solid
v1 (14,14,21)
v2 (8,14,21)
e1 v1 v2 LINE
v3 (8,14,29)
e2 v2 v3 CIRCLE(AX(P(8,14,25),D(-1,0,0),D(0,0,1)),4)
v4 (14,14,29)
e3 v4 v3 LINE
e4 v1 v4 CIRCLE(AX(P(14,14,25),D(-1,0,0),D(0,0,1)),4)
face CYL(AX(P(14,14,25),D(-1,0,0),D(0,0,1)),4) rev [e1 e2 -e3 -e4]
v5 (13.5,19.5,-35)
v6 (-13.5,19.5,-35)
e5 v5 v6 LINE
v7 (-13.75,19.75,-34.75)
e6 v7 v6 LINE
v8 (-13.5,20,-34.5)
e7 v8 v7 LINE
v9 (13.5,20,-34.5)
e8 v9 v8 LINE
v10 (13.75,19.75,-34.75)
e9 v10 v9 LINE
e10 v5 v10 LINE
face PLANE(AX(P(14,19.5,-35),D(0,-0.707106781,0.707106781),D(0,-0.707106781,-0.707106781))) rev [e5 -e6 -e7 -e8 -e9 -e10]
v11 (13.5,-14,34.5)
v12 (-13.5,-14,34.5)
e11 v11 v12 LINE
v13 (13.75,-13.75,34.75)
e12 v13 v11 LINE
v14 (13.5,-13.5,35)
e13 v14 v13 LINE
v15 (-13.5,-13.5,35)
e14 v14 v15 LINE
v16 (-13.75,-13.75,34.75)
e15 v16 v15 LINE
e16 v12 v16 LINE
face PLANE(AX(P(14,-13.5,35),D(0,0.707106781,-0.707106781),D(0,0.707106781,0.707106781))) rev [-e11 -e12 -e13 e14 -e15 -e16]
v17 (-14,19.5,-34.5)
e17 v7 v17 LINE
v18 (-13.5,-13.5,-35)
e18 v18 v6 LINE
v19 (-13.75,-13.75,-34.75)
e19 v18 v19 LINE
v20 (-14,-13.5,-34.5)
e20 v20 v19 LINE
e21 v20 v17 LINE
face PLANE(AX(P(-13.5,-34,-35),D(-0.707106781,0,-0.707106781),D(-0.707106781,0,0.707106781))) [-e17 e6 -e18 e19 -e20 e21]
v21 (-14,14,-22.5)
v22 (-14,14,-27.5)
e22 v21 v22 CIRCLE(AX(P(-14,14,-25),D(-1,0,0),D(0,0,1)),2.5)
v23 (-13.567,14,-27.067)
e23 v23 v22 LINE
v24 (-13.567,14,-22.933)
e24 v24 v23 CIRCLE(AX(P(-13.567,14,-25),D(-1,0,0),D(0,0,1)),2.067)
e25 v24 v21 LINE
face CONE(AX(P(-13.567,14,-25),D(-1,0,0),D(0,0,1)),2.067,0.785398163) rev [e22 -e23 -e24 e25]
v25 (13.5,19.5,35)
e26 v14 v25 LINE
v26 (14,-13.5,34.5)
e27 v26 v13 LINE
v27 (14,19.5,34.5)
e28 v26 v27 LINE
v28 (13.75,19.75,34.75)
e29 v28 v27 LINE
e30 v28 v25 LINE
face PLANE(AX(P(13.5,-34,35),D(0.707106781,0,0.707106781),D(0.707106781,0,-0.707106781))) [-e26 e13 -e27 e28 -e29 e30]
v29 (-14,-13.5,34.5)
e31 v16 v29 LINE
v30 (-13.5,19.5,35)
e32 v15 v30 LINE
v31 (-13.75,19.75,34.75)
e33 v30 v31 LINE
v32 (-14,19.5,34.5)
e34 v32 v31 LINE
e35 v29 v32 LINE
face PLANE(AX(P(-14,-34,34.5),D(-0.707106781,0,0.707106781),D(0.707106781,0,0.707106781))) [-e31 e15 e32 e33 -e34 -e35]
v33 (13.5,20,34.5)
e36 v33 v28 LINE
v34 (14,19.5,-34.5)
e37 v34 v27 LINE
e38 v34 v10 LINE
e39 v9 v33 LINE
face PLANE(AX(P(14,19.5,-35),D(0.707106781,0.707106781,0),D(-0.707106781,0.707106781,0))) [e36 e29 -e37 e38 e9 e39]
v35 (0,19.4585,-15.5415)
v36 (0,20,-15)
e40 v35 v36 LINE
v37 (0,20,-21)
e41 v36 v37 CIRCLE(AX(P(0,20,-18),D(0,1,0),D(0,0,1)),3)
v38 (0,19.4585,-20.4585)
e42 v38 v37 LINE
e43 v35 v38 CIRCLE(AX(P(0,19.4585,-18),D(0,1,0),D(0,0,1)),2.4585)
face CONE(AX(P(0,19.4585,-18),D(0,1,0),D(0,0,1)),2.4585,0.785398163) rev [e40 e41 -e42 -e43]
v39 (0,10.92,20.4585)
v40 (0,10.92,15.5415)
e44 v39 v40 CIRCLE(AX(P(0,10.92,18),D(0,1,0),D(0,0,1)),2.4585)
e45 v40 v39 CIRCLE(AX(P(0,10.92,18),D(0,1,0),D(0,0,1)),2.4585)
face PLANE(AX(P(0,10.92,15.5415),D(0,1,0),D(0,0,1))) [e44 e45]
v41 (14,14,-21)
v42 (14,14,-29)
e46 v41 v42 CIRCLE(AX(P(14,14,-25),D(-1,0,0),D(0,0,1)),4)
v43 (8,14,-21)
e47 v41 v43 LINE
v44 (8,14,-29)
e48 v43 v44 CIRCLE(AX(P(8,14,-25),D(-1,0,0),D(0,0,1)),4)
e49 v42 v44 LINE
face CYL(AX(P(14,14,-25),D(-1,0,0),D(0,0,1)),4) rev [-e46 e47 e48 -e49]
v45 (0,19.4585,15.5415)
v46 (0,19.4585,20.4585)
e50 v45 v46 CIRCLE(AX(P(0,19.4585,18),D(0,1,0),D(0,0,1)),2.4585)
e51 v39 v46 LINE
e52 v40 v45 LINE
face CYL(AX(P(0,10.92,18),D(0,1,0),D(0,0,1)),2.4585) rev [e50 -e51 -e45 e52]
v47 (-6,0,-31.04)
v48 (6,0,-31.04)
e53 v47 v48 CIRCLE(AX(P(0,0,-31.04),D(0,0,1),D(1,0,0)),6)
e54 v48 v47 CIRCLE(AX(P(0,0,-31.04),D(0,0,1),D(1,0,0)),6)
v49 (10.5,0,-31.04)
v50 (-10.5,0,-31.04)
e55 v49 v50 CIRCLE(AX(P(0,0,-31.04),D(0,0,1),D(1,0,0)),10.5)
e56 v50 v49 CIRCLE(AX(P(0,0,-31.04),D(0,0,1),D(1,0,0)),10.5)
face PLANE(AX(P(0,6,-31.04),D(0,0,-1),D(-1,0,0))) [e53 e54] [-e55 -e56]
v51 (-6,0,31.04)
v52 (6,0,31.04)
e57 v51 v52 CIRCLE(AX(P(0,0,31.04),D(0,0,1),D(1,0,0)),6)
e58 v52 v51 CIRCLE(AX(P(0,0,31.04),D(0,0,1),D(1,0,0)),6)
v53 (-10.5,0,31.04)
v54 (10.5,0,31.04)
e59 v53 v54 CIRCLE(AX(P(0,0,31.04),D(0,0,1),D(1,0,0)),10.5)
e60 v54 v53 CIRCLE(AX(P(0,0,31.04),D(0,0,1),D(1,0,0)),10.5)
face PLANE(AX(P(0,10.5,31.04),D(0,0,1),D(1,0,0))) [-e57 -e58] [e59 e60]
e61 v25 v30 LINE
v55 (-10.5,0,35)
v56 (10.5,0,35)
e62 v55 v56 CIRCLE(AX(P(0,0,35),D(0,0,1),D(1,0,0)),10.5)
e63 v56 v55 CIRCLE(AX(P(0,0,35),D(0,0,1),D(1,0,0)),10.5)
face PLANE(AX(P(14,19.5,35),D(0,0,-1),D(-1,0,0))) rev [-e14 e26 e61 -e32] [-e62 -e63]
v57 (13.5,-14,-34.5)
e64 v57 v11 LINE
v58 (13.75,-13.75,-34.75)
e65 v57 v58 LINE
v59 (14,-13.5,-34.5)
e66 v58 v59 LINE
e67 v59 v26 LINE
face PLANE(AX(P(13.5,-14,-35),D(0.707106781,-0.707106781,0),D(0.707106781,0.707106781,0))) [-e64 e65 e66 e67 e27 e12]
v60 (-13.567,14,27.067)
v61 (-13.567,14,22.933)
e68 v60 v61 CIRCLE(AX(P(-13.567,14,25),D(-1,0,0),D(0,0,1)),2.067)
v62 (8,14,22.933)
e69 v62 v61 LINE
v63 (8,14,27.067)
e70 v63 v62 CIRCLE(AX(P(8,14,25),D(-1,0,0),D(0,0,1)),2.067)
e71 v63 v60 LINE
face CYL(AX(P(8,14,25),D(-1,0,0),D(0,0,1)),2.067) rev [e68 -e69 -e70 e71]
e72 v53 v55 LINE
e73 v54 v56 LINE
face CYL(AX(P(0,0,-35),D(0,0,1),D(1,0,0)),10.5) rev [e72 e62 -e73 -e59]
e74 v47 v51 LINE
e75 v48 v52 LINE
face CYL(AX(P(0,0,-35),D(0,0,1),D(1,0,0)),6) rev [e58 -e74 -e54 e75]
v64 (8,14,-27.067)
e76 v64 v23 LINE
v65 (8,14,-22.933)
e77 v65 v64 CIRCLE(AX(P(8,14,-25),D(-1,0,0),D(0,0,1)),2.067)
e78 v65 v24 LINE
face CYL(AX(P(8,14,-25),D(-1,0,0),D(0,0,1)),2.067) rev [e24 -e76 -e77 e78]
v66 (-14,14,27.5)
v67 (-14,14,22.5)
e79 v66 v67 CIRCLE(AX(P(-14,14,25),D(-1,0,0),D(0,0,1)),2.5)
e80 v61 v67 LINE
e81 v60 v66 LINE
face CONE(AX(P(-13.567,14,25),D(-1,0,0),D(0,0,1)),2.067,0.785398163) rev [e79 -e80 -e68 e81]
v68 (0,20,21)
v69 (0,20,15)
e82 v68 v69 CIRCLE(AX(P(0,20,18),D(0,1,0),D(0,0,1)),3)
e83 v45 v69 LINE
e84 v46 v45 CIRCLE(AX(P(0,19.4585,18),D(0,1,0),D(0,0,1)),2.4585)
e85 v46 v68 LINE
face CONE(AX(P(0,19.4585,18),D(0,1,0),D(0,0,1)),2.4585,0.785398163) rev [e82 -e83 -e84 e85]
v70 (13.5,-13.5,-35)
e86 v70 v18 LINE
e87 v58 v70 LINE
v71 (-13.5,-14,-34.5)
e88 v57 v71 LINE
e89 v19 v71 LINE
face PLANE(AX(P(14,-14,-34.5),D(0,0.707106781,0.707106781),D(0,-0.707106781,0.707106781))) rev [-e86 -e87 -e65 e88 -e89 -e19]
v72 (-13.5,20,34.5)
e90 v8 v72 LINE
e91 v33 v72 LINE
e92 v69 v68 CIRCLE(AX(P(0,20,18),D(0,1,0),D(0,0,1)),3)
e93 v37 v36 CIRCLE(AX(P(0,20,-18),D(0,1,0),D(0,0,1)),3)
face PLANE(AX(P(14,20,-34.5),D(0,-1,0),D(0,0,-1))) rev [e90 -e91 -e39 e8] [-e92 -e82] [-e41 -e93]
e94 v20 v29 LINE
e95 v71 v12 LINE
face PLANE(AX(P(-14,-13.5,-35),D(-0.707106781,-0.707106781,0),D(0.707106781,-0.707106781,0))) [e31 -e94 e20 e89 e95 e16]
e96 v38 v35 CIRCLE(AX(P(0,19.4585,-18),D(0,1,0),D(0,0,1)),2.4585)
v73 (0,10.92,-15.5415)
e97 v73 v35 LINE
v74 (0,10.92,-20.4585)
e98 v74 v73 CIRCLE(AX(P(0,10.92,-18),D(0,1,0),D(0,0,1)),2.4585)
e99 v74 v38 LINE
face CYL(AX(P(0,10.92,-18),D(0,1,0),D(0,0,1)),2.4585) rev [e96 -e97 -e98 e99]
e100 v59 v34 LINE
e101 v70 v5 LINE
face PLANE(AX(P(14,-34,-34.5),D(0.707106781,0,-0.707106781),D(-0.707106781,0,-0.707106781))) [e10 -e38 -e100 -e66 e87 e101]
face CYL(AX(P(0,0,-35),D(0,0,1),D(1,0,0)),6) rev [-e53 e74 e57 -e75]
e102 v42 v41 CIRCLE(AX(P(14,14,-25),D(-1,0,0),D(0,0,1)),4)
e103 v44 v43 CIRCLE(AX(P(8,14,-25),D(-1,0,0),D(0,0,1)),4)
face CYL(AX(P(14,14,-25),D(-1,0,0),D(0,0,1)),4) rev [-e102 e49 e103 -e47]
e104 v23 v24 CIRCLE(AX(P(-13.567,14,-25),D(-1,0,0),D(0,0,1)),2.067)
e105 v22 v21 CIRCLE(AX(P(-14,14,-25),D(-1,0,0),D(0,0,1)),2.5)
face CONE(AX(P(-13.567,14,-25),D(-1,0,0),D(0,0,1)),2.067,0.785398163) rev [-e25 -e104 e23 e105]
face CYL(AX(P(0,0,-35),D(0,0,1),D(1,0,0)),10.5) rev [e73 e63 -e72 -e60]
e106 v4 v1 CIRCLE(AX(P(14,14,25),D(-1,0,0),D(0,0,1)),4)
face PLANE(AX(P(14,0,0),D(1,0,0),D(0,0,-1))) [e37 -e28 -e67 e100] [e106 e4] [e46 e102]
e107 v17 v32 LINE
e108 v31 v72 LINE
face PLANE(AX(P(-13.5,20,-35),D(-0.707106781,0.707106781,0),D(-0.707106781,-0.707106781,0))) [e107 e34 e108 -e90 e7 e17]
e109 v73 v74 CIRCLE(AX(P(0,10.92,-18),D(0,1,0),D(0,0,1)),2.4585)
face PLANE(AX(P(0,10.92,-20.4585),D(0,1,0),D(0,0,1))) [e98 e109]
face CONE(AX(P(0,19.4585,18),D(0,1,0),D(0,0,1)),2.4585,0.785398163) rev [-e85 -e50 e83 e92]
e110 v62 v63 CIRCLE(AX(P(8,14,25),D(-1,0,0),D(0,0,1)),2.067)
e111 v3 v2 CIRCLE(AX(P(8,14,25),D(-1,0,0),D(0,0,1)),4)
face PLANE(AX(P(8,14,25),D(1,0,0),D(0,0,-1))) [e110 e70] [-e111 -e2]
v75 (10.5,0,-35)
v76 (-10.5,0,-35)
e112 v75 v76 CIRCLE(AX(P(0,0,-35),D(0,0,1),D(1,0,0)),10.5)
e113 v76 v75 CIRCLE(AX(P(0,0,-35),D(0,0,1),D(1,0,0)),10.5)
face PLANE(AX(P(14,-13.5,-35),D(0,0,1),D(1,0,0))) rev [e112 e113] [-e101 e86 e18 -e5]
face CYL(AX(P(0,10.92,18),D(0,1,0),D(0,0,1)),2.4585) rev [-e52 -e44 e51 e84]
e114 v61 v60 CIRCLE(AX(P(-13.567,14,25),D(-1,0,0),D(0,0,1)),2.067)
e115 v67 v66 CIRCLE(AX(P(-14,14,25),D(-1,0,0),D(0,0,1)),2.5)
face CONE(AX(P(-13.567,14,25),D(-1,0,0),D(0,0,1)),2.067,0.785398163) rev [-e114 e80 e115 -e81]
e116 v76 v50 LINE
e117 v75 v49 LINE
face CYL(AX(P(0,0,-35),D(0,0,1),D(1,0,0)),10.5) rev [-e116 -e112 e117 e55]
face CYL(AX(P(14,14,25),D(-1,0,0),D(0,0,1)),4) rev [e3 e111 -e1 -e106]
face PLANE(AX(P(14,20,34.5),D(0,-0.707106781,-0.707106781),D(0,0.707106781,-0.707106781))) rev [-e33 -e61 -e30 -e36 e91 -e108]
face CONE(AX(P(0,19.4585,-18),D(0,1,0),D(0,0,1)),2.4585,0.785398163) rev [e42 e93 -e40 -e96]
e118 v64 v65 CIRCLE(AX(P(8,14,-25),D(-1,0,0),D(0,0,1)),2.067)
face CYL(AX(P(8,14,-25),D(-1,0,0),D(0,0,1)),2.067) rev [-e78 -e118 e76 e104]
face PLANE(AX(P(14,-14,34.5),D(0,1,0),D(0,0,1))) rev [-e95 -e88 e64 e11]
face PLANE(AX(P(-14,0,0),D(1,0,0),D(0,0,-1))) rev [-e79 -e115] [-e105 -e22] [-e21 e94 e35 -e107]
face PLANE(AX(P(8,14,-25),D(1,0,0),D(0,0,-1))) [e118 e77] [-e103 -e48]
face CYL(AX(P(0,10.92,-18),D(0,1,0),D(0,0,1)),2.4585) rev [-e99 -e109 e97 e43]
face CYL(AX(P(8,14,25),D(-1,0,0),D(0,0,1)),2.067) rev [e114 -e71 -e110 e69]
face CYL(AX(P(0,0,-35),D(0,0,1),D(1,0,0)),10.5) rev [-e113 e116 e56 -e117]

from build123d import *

# Parameters (mm, degrees)
EXTRUDE_1_DEPTH          = 14
EXTRUDE_1_DEPTH_BACK     = 14
SKETCH_3_W               = 6
SKETCH_3_H               = 4
SKETCH_4_W               = 6
SKETCH_4_H               = 4
CUT_EXTRUDE_1_DEPTH      = 35
CUT_EXTRUDE_1_DEPTH_BACK = 35
SKETCH_9_W               = 32
SKETCH_9_H               = 38
CUT_EXTRUDE_2_DEPTH      = 34
CUT_EXTRUDE_2_DEPTH_BACK = 34
SKETCH_10_W              = 32
SKETCH_10_H              = 74


with BuildPart() as part:
    # 草图1 → 凸台-拉伸1 (new, two sides: drawn at the far end of the back side and taken through both)
    with BuildSketch(Plane(origin=(0, 0, 0), x_dir=(0, 0, -1), z_dir=(1, 0, 0)).offset(-EXTRUDE_1_DEPTH_BACK)):
        Polygon((-35, -13.5), (-34.5, -14), (34.5, -14), (35, -13.5), (35, 19.5), (34.5, 20), (-34.5, 20), (-35, 19.5), align=None)
    extrude(amount=EXTRUDE_1_DEPTH + EXTRUDE_1_DEPTH_BACK)

    # 草图2 → 切除-旋转1 (revolve, cut)
    with BuildSketch(Plane(origin=(0, 0, 0), x_dir=(0, 0, -1), z_dir=(1, 0, 0)), mode=Mode.PRIVATE) as cut_revolve_1_sk:
        Polygon((-35, 0), (-35, 10.5), (-31.04, 10.5), (-31.04, 6), (31.04, 6), (31.04, 10.5), (35, 10.5), (35, 0), align=None)
    revolve(cut_revolve_1_sk.sketch.rotate(Axis((0, 0, -35), (0, 0, 1)), 270), axis=Axis((0, 0, -35), (0, 0, 1)), mode=Mode.SUBTRACT)

    # 草图3 → 切除-旋转2 (revolve, cut)
    with BuildSketch(Plane.XY.offset(25), mode=Mode.PRIVATE) as cut_revolve_2_sk:
        with Locations((11, 16)):
            Rectangle(SKETCH_3_W, SKETCH_3_H)
    revolve(cut_revolve_2_sk.sketch.rotate(Axis((14, 14, 25), (-1, 0, 0)), 270), axis=Axis((14, 14, 25), (-1, 0, 0)), mode=Mode.SUBTRACT)

    # 草图4 → 切除-旋转3 (revolve, cut)
    with BuildSketch(Plane.XY.offset(-25), mode=Mode.PRIVATE) as cut_revolve_3_sk:
        with Locations((11, 16)):
            Rectangle(SKETCH_4_W, SKETCH_4_H)
    revolve(cut_revolve_3_sk.sketch.rotate(Axis((14, 14, -25), (-1, 0, 0)), 270), axis=Axis((14, 14, -25), (-1, 0, 0)), mode=Mode.SUBTRACT)

    # 草图5 → 切除-旋转4 (revolve, cut)
    with BuildSketch(Plane(origin=(0, 0, 0), x_dir=(0, 0, -1), z_dir=(1, 0, 0)), mode=Mode.PRIVATE) as cut_revolve_4_sk:
        Polygon((18, 20), (21, 20), (20.4585, 19.4585), (20.4585, 10.92), (18, 10.92), align=None)
    revolve(cut_revolve_4_sk.sketch.rotate(Axis((0, 10.92, -18), (0, 1, 0)), 180), axis=Axis((0, 10.92, -18), (0, 1, 0)), mode=Mode.SUBTRACT)

    # 草图6 → 切除-旋转5 (revolve, cut)
    with BuildSketch(Plane(origin=(0, 0, 0), x_dir=(0, 0, -1), z_dir=(1, 0, 0)), mode=Mode.PRIVATE) as cut_revolve_5_sk:
        Polygon((-18, 20), (-15, 20), (-15.5415, 19.4585), (-15.5415, 10.92), (-18, 10.92), align=None)
    revolve(cut_revolve_5_sk.sketch.rotate(Axis((0, 10.92, 18), (0, 1, 0)), 180), axis=Axis((0, 10.92, 18), (0, 1, 0)), mode=Mode.SUBTRACT)

    # 草图7 → 切除-旋转6 (revolve, cut)
    with BuildSketch(Plane.XY.offset(-25), mode=Mode.PRIVATE) as cut_revolve_6_sk:
        Polygon((-14, 14), (-14, 16.5), (-13.567, 16.067), (8, 16.067), (8, 14), align=None)
    revolve(cut_revolve_6_sk.sketch.rotate(Axis((8, 14, -25), (-1, 0, 0)), 270), axis=Axis((8, 14, -25), (-1, 0, 0)), mode=Mode.SUBTRACT)

    # 草图8 → 切除-旋转7 (revolve, cut)
    with BuildSketch(Plane.XY.offset(25), mode=Mode.PRIVATE) as cut_revolve_7_sk:
        Polygon((-14, 14), (-14, 16.5), (-13.567, 16.067), (8, 16.067), (8, 14), align=None)
    revolve(cut_revolve_7_sk.sketch.rotate(Axis((8, 14, 25), (-1, 0, 0)), 270), axis=Axis((8, 14, 25), (-1, 0, 0)), mode=Mode.SUBTRACT)

    # 草图9 → 切除-拉伸1 (cut, two sides: drawn at the far end of the back side and taken through both)
    with BuildSketch(Plane.XY.offset(-CUT_EXTRUDE_1_DEPTH_BACK)):
        with Locations((0, 3)):
            Rectangle(SKETCH_9_W, SKETCH_9_H)
        Polygon((-14, -13.5), (-13.5, -14), (13.5, -14), (14, -13.5), (14, 19.5), (13.5, 20), (-13.5, 20), (-14, 19.5), align=None, mode=Mode.SUBTRACT)
    extrude(amount=CUT_EXTRUDE_1_DEPTH + CUT_EXTRUDE_1_DEPTH_BACK, mode=Mode.SUBTRACT)

    # 草图10 → 切除-拉伸2 (cut, two sides: drawn at the far end of the back side and taken through both)
    with BuildSketch(Plane(origin=(0, 0, 0), x_dir=(1, 0, 0), z_dir=(0, 1, 0)).offset(-CUT_EXTRUDE_2_DEPTH_BACK)):
        Rectangle(SKETCH_10_W, SKETCH_10_H)
        Polygon((-14, -34.5), (-13.5, -35), (13.5, -35), (14, -34.5), (14, 34.5), (13.5, 35), (-13.5, 35), (-14, 34.5), align=None, mode=Mode.SUBTRACT)
    extrude(amount=CUT_EXTRUDE_2_DEPTH + CUT_EXTRUDE_2_DEPTH_BACK, mode=Mode.SUBTRACT)


solid = part.part
